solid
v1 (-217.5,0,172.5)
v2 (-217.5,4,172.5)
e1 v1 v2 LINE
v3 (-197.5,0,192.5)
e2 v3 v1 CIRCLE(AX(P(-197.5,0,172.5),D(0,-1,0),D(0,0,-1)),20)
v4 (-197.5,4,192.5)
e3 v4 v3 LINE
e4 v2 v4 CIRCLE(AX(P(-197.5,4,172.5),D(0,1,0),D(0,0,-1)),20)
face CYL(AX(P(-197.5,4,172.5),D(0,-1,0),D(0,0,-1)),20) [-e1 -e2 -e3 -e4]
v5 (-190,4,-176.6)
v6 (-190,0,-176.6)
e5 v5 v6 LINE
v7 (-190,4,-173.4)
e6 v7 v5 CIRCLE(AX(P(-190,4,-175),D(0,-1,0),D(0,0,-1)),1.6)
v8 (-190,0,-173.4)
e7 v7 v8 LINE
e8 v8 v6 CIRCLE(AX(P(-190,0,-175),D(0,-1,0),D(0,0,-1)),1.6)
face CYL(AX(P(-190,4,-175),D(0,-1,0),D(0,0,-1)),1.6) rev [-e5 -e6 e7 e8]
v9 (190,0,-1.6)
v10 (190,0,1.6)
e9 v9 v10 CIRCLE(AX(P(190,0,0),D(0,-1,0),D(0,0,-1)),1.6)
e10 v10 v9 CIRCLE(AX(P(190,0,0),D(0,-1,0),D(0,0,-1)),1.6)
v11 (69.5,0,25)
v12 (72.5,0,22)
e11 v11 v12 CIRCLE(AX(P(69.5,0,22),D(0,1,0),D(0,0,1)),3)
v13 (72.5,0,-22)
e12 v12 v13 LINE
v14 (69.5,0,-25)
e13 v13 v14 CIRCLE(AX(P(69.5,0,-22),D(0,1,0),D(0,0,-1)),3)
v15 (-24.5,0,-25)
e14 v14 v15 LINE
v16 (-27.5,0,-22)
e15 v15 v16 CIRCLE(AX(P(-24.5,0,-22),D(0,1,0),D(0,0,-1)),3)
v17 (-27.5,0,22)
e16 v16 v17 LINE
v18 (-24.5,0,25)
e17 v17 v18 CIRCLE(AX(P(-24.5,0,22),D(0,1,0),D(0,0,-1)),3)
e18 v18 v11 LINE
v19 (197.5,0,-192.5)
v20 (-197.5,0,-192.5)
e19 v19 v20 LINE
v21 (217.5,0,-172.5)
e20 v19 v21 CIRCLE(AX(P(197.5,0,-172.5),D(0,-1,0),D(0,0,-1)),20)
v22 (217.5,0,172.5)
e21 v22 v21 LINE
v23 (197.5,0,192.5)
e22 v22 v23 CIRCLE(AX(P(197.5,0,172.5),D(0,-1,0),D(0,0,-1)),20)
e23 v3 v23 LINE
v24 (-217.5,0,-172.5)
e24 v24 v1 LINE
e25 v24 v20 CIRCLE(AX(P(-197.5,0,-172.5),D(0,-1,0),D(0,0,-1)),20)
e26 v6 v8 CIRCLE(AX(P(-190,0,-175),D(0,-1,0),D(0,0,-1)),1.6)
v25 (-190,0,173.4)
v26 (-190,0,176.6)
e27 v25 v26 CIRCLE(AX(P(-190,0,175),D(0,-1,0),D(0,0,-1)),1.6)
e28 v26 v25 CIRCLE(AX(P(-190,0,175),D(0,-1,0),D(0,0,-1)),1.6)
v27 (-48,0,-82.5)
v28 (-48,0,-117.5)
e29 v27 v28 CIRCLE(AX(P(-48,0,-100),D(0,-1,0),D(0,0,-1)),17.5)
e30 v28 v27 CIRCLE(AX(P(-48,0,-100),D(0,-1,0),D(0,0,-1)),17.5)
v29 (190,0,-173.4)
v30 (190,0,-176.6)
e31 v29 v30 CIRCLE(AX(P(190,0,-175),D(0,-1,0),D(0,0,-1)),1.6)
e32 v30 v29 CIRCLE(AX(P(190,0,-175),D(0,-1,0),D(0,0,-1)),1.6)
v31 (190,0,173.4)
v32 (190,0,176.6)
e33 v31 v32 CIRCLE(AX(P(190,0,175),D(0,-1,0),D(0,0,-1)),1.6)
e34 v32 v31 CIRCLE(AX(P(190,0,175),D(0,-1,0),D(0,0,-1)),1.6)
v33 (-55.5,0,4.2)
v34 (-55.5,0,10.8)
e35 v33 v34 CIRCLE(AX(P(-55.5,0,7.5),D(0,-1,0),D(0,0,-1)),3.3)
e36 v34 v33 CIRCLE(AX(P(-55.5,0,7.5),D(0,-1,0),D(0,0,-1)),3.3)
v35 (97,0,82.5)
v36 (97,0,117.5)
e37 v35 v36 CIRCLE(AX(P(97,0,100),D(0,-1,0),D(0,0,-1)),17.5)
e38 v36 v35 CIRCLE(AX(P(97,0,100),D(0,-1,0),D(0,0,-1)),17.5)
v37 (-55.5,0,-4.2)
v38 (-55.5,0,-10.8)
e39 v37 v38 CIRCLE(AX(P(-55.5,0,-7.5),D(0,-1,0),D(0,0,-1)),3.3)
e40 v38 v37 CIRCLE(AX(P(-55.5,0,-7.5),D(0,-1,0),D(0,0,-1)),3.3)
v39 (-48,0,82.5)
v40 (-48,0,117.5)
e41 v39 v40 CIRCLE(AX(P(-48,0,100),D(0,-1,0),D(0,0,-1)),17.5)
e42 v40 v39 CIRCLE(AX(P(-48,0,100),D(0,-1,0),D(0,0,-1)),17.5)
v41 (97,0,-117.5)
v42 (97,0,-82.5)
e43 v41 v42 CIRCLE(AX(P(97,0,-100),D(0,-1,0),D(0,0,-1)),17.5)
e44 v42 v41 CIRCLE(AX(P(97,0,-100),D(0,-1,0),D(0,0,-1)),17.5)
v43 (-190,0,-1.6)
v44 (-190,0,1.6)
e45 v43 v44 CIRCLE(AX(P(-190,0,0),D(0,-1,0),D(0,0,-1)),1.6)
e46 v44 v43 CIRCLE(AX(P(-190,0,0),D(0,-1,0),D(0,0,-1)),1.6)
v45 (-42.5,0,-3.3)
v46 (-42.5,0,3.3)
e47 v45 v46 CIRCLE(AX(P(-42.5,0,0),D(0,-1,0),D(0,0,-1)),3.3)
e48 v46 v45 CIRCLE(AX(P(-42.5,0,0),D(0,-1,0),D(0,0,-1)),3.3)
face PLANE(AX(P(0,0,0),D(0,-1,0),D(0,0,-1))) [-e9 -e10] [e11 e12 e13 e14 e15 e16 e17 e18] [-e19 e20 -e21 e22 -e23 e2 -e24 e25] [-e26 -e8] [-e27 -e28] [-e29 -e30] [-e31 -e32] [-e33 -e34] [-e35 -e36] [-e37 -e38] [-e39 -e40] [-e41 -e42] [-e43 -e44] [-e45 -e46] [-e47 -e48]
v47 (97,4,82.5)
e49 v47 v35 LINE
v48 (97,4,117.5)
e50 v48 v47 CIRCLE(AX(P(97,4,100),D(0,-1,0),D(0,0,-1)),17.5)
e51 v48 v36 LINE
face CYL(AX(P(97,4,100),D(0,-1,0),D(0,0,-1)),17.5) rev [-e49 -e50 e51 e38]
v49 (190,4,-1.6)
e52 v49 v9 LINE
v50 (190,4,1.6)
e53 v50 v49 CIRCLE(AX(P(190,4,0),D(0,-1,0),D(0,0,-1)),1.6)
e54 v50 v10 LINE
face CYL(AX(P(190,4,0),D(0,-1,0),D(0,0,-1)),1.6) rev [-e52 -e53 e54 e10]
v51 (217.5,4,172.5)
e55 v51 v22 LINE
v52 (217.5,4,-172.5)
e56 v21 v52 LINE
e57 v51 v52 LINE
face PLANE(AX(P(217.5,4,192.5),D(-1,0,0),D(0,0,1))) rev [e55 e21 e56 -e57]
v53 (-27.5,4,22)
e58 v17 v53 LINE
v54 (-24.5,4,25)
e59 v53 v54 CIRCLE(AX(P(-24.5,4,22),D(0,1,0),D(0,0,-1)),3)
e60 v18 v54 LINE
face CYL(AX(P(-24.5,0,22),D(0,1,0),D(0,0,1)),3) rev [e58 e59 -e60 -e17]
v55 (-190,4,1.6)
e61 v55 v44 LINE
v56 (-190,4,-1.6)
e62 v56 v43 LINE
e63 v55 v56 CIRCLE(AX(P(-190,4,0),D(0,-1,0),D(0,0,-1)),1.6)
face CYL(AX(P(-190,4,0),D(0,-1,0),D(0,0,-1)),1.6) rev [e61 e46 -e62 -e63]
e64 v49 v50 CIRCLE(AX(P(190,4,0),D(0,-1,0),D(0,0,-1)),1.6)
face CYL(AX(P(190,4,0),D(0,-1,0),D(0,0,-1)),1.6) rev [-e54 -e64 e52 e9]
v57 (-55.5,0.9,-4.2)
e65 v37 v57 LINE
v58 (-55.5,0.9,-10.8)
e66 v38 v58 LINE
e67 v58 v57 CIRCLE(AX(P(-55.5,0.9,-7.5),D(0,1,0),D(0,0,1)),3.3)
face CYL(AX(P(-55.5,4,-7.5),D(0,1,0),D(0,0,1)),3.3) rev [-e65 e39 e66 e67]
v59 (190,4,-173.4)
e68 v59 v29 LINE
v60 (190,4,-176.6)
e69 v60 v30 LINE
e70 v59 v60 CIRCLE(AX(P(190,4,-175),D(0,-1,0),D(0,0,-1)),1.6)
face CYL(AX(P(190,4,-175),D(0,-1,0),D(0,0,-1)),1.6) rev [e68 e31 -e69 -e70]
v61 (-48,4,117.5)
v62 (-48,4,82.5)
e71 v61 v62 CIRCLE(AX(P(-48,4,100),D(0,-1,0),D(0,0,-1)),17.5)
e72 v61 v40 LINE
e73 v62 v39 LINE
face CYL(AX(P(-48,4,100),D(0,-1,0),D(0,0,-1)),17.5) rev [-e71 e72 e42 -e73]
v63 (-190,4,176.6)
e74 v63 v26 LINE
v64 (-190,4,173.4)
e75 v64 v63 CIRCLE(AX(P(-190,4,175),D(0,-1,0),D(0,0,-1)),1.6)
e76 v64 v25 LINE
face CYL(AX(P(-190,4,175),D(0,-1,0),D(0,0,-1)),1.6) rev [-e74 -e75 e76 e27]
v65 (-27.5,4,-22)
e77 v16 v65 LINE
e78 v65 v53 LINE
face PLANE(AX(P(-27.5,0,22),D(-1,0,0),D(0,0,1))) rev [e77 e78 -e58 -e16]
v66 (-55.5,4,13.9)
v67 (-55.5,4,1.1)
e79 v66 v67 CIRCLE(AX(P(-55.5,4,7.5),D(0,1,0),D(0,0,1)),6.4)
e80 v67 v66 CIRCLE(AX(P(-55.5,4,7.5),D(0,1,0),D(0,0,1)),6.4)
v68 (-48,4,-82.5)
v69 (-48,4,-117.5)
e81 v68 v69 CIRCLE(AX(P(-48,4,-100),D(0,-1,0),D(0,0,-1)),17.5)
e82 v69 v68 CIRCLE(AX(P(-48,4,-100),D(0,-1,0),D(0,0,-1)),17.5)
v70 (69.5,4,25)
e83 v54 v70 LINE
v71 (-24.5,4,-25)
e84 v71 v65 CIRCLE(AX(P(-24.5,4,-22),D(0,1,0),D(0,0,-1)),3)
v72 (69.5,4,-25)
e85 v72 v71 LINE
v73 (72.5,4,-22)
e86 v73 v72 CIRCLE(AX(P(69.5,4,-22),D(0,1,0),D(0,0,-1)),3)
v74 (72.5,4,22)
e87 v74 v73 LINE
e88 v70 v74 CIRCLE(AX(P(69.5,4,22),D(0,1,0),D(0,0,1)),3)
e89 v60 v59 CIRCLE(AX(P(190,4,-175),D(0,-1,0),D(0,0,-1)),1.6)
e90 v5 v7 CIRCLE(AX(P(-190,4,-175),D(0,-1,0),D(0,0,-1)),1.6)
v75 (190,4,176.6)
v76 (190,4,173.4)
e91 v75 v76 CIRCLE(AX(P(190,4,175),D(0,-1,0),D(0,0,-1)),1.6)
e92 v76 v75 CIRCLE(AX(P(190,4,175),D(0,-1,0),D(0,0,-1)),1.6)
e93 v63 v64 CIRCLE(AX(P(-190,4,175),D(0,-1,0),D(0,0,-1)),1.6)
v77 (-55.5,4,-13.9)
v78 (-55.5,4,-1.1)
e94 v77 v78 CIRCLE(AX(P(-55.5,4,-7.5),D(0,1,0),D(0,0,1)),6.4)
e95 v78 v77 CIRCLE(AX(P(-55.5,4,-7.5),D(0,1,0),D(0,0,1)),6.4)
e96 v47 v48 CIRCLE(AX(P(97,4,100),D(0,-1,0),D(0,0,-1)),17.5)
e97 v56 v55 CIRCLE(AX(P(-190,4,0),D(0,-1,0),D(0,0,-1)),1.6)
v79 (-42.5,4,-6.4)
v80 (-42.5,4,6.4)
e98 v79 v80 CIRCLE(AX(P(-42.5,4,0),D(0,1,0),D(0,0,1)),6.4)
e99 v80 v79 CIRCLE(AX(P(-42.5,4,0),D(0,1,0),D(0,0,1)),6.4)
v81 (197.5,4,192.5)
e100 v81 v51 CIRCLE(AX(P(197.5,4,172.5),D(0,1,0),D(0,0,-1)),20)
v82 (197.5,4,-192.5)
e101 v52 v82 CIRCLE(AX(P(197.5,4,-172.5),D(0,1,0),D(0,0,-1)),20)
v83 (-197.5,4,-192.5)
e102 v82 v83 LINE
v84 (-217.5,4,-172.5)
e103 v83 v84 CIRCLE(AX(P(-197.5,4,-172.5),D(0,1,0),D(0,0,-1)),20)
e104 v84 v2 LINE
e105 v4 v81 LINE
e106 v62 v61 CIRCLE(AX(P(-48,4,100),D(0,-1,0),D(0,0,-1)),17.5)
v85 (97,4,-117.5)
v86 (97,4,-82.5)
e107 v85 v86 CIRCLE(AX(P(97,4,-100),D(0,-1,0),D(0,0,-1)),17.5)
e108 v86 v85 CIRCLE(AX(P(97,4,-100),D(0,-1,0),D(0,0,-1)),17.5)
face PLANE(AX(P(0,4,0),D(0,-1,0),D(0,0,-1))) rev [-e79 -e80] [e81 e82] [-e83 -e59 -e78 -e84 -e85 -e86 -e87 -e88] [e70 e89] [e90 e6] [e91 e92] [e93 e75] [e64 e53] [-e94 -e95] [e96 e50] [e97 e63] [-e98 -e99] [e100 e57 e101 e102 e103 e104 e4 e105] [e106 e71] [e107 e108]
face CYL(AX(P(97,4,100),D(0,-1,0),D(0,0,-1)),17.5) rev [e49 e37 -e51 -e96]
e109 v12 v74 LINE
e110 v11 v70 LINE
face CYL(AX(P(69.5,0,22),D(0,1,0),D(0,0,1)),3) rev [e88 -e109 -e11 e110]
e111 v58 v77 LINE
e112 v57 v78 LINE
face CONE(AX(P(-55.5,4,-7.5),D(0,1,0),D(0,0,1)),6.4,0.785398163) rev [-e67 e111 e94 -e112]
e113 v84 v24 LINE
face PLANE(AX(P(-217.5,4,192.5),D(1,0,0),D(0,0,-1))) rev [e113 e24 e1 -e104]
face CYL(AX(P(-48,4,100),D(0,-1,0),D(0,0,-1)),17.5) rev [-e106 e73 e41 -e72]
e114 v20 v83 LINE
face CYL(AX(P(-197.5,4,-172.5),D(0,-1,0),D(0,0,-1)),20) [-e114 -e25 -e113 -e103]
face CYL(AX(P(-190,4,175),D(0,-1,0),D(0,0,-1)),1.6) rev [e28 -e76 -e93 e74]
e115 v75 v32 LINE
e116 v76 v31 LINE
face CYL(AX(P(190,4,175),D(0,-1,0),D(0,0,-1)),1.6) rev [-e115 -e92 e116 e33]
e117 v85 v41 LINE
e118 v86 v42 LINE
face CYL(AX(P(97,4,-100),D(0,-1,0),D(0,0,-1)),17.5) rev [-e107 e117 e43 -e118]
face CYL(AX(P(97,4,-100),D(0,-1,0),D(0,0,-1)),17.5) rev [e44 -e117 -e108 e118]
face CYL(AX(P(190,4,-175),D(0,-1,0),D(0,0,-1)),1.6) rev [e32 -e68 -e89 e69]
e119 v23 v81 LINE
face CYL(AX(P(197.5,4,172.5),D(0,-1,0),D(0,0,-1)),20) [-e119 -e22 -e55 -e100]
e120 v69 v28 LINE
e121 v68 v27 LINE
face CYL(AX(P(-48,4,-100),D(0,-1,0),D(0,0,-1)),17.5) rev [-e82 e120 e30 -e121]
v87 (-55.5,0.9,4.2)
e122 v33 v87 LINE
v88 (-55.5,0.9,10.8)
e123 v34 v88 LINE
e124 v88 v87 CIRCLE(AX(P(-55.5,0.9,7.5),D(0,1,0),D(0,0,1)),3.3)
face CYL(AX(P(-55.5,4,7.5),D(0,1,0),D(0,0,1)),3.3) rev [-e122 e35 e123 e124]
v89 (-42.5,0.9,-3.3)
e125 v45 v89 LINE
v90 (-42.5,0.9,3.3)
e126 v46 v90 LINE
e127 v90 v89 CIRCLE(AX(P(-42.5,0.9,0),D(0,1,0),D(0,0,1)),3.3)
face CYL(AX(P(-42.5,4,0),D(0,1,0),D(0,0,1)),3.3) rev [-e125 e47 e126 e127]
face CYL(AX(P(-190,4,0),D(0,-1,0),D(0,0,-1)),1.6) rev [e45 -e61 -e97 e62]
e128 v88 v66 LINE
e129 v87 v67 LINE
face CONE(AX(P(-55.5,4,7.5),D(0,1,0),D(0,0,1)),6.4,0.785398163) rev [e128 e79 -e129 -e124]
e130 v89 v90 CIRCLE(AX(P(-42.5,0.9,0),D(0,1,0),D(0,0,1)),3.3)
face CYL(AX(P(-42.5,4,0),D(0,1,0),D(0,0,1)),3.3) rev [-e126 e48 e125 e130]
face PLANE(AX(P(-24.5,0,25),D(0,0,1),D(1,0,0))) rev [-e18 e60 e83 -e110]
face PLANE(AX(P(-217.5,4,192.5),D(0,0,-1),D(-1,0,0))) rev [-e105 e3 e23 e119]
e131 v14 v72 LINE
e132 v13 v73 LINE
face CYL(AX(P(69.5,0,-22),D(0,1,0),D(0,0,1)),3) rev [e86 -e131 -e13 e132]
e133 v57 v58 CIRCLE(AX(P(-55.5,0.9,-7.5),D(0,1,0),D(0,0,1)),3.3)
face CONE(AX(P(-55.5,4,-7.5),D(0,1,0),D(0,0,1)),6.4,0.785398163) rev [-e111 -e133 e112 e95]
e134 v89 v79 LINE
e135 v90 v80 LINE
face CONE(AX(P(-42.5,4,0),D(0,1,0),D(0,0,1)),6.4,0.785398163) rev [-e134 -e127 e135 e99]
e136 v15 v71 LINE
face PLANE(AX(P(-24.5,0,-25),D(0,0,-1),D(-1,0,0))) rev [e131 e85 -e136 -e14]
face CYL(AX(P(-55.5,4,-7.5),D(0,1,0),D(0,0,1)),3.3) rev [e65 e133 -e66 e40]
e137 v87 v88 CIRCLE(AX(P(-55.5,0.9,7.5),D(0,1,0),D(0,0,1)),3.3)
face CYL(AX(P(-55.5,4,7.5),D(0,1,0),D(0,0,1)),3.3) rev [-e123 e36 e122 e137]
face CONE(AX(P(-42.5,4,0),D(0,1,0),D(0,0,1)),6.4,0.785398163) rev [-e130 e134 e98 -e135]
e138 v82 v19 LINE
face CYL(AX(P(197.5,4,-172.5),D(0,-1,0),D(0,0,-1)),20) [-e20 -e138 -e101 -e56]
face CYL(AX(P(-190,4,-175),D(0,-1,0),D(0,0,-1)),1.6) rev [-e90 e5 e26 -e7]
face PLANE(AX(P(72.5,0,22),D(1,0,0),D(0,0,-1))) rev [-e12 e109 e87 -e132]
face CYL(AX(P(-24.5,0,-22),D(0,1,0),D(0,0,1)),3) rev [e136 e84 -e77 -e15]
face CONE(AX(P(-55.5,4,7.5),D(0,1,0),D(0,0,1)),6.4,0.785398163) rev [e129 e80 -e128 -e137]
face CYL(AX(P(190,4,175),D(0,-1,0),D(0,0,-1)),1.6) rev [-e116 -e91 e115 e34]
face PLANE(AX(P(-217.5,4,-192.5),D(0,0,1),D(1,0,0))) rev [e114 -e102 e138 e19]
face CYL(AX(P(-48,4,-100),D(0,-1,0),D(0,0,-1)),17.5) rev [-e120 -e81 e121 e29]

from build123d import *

# Parameters (mm, degrees)
SKETCH1_W                                        = 435
SKETCH1_H                                        = 385
BOSS_EXTRUDE1_DEPTH                              = 4
FILLET1_R                                        = 20
SKETCH2_R                                        = 1.555451355
SKETCH2_R_2                                      = 1.5
SKETCH2_R_3                                      = 1.924870622
CUT_EXTRUDE1_DEPTH                               = 10
CUT_EXTRUDE2_DEPTH                               = 4
HOLE_SIZE_BY_HEXALOBULAR_COUNTERSUNK_D           = 6.6
HOLE_SIZE_BY_HEXALOBULAR_COUNTERSUNK_DEPTH       = 7.5
HOLE_SIZE_BY_HEXALOBULAR_COUNTERSUNK_CSINK_D     = 12.8
HOLE_SIZE_BY_HEXALOBULAR_COUNTERSUNK_CSINK_ANGLE = 90
HOLE_SIZE_BY_HEXALOBULAR_COUNTERSUNK_TIP         = 1.982840043
SKETCH6_R                                        = 17.5
CUT_EXTRUDE3_DEPTH                               = 4
SKETCH7_R                                        = 1.6
CUT_EXTRUDE4_DEPTH                               = 4


with BuildPart() as part:
    # Sketch1 → Boss-Extrude1 (new body)
    with BuildSketch(Plane(origin=(0, 0, 0), x_dir=(1, 0, 0), z_dir=(0, 1, 0))):
        Rectangle(SKETCH1_W, SKETCH1_H)
    extrude(amount=BOSS_EXTRUDE1_DEPTH)

    # Fillet1
    fillet1_edges = [part.edges().sort_by_distance(p)[0] for p in [
        (217.5, 2, 192.5),
        (-217.5, 2, 192.5),
        (-217.5, 2, -192.5),
        (217.5, 2, -192.5),
    ]]
    fillet(fillet1_edges, radius=FILLET1_R)

    # Sketch2 → Cut-Extrude1 (cut)
    with BuildSketch(Plane(origin=(0, 4, 0), x_dir=(1, 0, 0), z_dir=(0, 1, 0))):
        with Locations(Location((-42.5, 0, 0), (0, 0, 270))):
            Circle(SKETCH2_R)
        with Locations(Location((-55.5, 7.5, 0), (0, 0, 270))):
            Circle(SKETCH2_R_2)
        with Locations(Location((-55.5, -7.5, 0), (0, 0, 270))):
            Circle(SKETCH2_R_3)
    extrude(amount=-CUT_EXTRUDE1_DEPTH, mode=Mode.SUBTRACT)

    # Sketch3 → Cut-Extrude2 (cut)
    with BuildSketch(Plane(origin=(0, 4, 0), x_dir=(1, 0, 0), z_dir=(0, 1, 0))):
        with BuildLine():
            Line((-24.5, -25), (69.5, -25))
            ThreePointArc((69.5, -25), (71.621320344, -24.121320344), (72.5, -22))
            Line((72.5, -22), (72.5, 22))
            ThreePointArc((72.5, 22), (71.621320344, 24.121320344), (69.5, 25))
            Line((69.5, 25), (-24.5, 25))
            ThreePointArc((-24.5, 25), (-26.621320344, 24.121320344), (-27.5, 22))
            Line((-27.5, 22), (-27.5, -22))
            ThreePointArc((-27.5, -22), (-26.621320344, -24.121320344), (-24.5, -25))
        make_face()
    extrude(amount=-CUT_EXTRUDE2_DEPTH, mode=Mode.SUBTRACT)

    # Hole Size (% by) Hexalobular Countersunk Head Screw Type1
    with Locations(Plane(origin=(0, 4, 0), x_dir=(1, 0, 0), z_dir=(0, 1, 0))):
        with Locations((-55.5, -7.5), (-42.5, 0), (-55.5, 7.5)):
            CounterSinkHole(HOLE_SIZE_BY_HEXALOBULAR_COUNTERSUNK_D / 2, HOLE_SIZE_BY_HEXALOBULAR_COUNTERSUNK_CSINK_D / 2, depth=HOLE_SIZE_BY_HEXALOBULAR_COUNTERSUNK_DEPTH, counter_sink_angle=HOLE_SIZE_BY_HEXALOBULAR_COUNTERSUNK_CSINK_ANGLE)
            with Locations((0, 0, -(HOLE_SIZE_BY_HEXALOBULAR_COUNTERSUNK_DEPTH + HOLE_SIZE_BY_HEXALOBULAR_COUNTERSUNK_TIP / 2))):  # 118° drill point
                Cone(0, HOLE_SIZE_BY_HEXALOBULAR_COUNTERSUNK_D / 2, HOLE_SIZE_BY_HEXALOBULAR_COUNTERSUNK_TIP, mode=Mode.SUBTRACT)

    # Sketch6 → Cut-Extrude3 (cut)
    with BuildSketch(Plane.XZ):
        with Locations(Location((-48, 100, 0), (0, 0, 270))):
            Circle(SKETCH6_R)
        with Locations(Location((97, 100, 0), (0, 0, 270))):
            Circle(SKETCH6_R)
        with Locations(Location((-48, -100, 0), (0, 0, 270))):
            Circle(SKETCH6_R)
        with Locations(Location((97, -100, 0), (0, 0, 270))):
            Circle(SKETCH6_R)
    extrude(amount=-CUT_EXTRUDE3_DEPTH, mode=Mode.SUBTRACT)

    # Sketch7 → Cut-Extrude4 (cut)
    with BuildSketch(Plane.XZ):
        with Locations(Location((-190, 175, 0), (0, 0, 270))):
            Circle(SKETCH7_R)
        with Locations(Location((-190, 0, 0), (0, 0, 270))):
            Circle(SKETCH7_R)
        with Locations(Location((-190, -175, 0), (0, 0, 270))):
            Circle(SKETCH7_R)
        with Locations(Location((190, 175, 0), (0, 0, 270))):
            Circle(SKETCH7_R)
        with Locations(Location((190, 0, 0), (0, 0, 270))):
            Circle(SKETCH7_R)
        with Locations(Location((190, -175, 0), (0, 0, 270))):
            Circle(SKETCH7_R)
    extrude(amount=-CUT_EXTRUDE4_DEPTH, mode=Mode.SUBTRACT)


solid = part.part
